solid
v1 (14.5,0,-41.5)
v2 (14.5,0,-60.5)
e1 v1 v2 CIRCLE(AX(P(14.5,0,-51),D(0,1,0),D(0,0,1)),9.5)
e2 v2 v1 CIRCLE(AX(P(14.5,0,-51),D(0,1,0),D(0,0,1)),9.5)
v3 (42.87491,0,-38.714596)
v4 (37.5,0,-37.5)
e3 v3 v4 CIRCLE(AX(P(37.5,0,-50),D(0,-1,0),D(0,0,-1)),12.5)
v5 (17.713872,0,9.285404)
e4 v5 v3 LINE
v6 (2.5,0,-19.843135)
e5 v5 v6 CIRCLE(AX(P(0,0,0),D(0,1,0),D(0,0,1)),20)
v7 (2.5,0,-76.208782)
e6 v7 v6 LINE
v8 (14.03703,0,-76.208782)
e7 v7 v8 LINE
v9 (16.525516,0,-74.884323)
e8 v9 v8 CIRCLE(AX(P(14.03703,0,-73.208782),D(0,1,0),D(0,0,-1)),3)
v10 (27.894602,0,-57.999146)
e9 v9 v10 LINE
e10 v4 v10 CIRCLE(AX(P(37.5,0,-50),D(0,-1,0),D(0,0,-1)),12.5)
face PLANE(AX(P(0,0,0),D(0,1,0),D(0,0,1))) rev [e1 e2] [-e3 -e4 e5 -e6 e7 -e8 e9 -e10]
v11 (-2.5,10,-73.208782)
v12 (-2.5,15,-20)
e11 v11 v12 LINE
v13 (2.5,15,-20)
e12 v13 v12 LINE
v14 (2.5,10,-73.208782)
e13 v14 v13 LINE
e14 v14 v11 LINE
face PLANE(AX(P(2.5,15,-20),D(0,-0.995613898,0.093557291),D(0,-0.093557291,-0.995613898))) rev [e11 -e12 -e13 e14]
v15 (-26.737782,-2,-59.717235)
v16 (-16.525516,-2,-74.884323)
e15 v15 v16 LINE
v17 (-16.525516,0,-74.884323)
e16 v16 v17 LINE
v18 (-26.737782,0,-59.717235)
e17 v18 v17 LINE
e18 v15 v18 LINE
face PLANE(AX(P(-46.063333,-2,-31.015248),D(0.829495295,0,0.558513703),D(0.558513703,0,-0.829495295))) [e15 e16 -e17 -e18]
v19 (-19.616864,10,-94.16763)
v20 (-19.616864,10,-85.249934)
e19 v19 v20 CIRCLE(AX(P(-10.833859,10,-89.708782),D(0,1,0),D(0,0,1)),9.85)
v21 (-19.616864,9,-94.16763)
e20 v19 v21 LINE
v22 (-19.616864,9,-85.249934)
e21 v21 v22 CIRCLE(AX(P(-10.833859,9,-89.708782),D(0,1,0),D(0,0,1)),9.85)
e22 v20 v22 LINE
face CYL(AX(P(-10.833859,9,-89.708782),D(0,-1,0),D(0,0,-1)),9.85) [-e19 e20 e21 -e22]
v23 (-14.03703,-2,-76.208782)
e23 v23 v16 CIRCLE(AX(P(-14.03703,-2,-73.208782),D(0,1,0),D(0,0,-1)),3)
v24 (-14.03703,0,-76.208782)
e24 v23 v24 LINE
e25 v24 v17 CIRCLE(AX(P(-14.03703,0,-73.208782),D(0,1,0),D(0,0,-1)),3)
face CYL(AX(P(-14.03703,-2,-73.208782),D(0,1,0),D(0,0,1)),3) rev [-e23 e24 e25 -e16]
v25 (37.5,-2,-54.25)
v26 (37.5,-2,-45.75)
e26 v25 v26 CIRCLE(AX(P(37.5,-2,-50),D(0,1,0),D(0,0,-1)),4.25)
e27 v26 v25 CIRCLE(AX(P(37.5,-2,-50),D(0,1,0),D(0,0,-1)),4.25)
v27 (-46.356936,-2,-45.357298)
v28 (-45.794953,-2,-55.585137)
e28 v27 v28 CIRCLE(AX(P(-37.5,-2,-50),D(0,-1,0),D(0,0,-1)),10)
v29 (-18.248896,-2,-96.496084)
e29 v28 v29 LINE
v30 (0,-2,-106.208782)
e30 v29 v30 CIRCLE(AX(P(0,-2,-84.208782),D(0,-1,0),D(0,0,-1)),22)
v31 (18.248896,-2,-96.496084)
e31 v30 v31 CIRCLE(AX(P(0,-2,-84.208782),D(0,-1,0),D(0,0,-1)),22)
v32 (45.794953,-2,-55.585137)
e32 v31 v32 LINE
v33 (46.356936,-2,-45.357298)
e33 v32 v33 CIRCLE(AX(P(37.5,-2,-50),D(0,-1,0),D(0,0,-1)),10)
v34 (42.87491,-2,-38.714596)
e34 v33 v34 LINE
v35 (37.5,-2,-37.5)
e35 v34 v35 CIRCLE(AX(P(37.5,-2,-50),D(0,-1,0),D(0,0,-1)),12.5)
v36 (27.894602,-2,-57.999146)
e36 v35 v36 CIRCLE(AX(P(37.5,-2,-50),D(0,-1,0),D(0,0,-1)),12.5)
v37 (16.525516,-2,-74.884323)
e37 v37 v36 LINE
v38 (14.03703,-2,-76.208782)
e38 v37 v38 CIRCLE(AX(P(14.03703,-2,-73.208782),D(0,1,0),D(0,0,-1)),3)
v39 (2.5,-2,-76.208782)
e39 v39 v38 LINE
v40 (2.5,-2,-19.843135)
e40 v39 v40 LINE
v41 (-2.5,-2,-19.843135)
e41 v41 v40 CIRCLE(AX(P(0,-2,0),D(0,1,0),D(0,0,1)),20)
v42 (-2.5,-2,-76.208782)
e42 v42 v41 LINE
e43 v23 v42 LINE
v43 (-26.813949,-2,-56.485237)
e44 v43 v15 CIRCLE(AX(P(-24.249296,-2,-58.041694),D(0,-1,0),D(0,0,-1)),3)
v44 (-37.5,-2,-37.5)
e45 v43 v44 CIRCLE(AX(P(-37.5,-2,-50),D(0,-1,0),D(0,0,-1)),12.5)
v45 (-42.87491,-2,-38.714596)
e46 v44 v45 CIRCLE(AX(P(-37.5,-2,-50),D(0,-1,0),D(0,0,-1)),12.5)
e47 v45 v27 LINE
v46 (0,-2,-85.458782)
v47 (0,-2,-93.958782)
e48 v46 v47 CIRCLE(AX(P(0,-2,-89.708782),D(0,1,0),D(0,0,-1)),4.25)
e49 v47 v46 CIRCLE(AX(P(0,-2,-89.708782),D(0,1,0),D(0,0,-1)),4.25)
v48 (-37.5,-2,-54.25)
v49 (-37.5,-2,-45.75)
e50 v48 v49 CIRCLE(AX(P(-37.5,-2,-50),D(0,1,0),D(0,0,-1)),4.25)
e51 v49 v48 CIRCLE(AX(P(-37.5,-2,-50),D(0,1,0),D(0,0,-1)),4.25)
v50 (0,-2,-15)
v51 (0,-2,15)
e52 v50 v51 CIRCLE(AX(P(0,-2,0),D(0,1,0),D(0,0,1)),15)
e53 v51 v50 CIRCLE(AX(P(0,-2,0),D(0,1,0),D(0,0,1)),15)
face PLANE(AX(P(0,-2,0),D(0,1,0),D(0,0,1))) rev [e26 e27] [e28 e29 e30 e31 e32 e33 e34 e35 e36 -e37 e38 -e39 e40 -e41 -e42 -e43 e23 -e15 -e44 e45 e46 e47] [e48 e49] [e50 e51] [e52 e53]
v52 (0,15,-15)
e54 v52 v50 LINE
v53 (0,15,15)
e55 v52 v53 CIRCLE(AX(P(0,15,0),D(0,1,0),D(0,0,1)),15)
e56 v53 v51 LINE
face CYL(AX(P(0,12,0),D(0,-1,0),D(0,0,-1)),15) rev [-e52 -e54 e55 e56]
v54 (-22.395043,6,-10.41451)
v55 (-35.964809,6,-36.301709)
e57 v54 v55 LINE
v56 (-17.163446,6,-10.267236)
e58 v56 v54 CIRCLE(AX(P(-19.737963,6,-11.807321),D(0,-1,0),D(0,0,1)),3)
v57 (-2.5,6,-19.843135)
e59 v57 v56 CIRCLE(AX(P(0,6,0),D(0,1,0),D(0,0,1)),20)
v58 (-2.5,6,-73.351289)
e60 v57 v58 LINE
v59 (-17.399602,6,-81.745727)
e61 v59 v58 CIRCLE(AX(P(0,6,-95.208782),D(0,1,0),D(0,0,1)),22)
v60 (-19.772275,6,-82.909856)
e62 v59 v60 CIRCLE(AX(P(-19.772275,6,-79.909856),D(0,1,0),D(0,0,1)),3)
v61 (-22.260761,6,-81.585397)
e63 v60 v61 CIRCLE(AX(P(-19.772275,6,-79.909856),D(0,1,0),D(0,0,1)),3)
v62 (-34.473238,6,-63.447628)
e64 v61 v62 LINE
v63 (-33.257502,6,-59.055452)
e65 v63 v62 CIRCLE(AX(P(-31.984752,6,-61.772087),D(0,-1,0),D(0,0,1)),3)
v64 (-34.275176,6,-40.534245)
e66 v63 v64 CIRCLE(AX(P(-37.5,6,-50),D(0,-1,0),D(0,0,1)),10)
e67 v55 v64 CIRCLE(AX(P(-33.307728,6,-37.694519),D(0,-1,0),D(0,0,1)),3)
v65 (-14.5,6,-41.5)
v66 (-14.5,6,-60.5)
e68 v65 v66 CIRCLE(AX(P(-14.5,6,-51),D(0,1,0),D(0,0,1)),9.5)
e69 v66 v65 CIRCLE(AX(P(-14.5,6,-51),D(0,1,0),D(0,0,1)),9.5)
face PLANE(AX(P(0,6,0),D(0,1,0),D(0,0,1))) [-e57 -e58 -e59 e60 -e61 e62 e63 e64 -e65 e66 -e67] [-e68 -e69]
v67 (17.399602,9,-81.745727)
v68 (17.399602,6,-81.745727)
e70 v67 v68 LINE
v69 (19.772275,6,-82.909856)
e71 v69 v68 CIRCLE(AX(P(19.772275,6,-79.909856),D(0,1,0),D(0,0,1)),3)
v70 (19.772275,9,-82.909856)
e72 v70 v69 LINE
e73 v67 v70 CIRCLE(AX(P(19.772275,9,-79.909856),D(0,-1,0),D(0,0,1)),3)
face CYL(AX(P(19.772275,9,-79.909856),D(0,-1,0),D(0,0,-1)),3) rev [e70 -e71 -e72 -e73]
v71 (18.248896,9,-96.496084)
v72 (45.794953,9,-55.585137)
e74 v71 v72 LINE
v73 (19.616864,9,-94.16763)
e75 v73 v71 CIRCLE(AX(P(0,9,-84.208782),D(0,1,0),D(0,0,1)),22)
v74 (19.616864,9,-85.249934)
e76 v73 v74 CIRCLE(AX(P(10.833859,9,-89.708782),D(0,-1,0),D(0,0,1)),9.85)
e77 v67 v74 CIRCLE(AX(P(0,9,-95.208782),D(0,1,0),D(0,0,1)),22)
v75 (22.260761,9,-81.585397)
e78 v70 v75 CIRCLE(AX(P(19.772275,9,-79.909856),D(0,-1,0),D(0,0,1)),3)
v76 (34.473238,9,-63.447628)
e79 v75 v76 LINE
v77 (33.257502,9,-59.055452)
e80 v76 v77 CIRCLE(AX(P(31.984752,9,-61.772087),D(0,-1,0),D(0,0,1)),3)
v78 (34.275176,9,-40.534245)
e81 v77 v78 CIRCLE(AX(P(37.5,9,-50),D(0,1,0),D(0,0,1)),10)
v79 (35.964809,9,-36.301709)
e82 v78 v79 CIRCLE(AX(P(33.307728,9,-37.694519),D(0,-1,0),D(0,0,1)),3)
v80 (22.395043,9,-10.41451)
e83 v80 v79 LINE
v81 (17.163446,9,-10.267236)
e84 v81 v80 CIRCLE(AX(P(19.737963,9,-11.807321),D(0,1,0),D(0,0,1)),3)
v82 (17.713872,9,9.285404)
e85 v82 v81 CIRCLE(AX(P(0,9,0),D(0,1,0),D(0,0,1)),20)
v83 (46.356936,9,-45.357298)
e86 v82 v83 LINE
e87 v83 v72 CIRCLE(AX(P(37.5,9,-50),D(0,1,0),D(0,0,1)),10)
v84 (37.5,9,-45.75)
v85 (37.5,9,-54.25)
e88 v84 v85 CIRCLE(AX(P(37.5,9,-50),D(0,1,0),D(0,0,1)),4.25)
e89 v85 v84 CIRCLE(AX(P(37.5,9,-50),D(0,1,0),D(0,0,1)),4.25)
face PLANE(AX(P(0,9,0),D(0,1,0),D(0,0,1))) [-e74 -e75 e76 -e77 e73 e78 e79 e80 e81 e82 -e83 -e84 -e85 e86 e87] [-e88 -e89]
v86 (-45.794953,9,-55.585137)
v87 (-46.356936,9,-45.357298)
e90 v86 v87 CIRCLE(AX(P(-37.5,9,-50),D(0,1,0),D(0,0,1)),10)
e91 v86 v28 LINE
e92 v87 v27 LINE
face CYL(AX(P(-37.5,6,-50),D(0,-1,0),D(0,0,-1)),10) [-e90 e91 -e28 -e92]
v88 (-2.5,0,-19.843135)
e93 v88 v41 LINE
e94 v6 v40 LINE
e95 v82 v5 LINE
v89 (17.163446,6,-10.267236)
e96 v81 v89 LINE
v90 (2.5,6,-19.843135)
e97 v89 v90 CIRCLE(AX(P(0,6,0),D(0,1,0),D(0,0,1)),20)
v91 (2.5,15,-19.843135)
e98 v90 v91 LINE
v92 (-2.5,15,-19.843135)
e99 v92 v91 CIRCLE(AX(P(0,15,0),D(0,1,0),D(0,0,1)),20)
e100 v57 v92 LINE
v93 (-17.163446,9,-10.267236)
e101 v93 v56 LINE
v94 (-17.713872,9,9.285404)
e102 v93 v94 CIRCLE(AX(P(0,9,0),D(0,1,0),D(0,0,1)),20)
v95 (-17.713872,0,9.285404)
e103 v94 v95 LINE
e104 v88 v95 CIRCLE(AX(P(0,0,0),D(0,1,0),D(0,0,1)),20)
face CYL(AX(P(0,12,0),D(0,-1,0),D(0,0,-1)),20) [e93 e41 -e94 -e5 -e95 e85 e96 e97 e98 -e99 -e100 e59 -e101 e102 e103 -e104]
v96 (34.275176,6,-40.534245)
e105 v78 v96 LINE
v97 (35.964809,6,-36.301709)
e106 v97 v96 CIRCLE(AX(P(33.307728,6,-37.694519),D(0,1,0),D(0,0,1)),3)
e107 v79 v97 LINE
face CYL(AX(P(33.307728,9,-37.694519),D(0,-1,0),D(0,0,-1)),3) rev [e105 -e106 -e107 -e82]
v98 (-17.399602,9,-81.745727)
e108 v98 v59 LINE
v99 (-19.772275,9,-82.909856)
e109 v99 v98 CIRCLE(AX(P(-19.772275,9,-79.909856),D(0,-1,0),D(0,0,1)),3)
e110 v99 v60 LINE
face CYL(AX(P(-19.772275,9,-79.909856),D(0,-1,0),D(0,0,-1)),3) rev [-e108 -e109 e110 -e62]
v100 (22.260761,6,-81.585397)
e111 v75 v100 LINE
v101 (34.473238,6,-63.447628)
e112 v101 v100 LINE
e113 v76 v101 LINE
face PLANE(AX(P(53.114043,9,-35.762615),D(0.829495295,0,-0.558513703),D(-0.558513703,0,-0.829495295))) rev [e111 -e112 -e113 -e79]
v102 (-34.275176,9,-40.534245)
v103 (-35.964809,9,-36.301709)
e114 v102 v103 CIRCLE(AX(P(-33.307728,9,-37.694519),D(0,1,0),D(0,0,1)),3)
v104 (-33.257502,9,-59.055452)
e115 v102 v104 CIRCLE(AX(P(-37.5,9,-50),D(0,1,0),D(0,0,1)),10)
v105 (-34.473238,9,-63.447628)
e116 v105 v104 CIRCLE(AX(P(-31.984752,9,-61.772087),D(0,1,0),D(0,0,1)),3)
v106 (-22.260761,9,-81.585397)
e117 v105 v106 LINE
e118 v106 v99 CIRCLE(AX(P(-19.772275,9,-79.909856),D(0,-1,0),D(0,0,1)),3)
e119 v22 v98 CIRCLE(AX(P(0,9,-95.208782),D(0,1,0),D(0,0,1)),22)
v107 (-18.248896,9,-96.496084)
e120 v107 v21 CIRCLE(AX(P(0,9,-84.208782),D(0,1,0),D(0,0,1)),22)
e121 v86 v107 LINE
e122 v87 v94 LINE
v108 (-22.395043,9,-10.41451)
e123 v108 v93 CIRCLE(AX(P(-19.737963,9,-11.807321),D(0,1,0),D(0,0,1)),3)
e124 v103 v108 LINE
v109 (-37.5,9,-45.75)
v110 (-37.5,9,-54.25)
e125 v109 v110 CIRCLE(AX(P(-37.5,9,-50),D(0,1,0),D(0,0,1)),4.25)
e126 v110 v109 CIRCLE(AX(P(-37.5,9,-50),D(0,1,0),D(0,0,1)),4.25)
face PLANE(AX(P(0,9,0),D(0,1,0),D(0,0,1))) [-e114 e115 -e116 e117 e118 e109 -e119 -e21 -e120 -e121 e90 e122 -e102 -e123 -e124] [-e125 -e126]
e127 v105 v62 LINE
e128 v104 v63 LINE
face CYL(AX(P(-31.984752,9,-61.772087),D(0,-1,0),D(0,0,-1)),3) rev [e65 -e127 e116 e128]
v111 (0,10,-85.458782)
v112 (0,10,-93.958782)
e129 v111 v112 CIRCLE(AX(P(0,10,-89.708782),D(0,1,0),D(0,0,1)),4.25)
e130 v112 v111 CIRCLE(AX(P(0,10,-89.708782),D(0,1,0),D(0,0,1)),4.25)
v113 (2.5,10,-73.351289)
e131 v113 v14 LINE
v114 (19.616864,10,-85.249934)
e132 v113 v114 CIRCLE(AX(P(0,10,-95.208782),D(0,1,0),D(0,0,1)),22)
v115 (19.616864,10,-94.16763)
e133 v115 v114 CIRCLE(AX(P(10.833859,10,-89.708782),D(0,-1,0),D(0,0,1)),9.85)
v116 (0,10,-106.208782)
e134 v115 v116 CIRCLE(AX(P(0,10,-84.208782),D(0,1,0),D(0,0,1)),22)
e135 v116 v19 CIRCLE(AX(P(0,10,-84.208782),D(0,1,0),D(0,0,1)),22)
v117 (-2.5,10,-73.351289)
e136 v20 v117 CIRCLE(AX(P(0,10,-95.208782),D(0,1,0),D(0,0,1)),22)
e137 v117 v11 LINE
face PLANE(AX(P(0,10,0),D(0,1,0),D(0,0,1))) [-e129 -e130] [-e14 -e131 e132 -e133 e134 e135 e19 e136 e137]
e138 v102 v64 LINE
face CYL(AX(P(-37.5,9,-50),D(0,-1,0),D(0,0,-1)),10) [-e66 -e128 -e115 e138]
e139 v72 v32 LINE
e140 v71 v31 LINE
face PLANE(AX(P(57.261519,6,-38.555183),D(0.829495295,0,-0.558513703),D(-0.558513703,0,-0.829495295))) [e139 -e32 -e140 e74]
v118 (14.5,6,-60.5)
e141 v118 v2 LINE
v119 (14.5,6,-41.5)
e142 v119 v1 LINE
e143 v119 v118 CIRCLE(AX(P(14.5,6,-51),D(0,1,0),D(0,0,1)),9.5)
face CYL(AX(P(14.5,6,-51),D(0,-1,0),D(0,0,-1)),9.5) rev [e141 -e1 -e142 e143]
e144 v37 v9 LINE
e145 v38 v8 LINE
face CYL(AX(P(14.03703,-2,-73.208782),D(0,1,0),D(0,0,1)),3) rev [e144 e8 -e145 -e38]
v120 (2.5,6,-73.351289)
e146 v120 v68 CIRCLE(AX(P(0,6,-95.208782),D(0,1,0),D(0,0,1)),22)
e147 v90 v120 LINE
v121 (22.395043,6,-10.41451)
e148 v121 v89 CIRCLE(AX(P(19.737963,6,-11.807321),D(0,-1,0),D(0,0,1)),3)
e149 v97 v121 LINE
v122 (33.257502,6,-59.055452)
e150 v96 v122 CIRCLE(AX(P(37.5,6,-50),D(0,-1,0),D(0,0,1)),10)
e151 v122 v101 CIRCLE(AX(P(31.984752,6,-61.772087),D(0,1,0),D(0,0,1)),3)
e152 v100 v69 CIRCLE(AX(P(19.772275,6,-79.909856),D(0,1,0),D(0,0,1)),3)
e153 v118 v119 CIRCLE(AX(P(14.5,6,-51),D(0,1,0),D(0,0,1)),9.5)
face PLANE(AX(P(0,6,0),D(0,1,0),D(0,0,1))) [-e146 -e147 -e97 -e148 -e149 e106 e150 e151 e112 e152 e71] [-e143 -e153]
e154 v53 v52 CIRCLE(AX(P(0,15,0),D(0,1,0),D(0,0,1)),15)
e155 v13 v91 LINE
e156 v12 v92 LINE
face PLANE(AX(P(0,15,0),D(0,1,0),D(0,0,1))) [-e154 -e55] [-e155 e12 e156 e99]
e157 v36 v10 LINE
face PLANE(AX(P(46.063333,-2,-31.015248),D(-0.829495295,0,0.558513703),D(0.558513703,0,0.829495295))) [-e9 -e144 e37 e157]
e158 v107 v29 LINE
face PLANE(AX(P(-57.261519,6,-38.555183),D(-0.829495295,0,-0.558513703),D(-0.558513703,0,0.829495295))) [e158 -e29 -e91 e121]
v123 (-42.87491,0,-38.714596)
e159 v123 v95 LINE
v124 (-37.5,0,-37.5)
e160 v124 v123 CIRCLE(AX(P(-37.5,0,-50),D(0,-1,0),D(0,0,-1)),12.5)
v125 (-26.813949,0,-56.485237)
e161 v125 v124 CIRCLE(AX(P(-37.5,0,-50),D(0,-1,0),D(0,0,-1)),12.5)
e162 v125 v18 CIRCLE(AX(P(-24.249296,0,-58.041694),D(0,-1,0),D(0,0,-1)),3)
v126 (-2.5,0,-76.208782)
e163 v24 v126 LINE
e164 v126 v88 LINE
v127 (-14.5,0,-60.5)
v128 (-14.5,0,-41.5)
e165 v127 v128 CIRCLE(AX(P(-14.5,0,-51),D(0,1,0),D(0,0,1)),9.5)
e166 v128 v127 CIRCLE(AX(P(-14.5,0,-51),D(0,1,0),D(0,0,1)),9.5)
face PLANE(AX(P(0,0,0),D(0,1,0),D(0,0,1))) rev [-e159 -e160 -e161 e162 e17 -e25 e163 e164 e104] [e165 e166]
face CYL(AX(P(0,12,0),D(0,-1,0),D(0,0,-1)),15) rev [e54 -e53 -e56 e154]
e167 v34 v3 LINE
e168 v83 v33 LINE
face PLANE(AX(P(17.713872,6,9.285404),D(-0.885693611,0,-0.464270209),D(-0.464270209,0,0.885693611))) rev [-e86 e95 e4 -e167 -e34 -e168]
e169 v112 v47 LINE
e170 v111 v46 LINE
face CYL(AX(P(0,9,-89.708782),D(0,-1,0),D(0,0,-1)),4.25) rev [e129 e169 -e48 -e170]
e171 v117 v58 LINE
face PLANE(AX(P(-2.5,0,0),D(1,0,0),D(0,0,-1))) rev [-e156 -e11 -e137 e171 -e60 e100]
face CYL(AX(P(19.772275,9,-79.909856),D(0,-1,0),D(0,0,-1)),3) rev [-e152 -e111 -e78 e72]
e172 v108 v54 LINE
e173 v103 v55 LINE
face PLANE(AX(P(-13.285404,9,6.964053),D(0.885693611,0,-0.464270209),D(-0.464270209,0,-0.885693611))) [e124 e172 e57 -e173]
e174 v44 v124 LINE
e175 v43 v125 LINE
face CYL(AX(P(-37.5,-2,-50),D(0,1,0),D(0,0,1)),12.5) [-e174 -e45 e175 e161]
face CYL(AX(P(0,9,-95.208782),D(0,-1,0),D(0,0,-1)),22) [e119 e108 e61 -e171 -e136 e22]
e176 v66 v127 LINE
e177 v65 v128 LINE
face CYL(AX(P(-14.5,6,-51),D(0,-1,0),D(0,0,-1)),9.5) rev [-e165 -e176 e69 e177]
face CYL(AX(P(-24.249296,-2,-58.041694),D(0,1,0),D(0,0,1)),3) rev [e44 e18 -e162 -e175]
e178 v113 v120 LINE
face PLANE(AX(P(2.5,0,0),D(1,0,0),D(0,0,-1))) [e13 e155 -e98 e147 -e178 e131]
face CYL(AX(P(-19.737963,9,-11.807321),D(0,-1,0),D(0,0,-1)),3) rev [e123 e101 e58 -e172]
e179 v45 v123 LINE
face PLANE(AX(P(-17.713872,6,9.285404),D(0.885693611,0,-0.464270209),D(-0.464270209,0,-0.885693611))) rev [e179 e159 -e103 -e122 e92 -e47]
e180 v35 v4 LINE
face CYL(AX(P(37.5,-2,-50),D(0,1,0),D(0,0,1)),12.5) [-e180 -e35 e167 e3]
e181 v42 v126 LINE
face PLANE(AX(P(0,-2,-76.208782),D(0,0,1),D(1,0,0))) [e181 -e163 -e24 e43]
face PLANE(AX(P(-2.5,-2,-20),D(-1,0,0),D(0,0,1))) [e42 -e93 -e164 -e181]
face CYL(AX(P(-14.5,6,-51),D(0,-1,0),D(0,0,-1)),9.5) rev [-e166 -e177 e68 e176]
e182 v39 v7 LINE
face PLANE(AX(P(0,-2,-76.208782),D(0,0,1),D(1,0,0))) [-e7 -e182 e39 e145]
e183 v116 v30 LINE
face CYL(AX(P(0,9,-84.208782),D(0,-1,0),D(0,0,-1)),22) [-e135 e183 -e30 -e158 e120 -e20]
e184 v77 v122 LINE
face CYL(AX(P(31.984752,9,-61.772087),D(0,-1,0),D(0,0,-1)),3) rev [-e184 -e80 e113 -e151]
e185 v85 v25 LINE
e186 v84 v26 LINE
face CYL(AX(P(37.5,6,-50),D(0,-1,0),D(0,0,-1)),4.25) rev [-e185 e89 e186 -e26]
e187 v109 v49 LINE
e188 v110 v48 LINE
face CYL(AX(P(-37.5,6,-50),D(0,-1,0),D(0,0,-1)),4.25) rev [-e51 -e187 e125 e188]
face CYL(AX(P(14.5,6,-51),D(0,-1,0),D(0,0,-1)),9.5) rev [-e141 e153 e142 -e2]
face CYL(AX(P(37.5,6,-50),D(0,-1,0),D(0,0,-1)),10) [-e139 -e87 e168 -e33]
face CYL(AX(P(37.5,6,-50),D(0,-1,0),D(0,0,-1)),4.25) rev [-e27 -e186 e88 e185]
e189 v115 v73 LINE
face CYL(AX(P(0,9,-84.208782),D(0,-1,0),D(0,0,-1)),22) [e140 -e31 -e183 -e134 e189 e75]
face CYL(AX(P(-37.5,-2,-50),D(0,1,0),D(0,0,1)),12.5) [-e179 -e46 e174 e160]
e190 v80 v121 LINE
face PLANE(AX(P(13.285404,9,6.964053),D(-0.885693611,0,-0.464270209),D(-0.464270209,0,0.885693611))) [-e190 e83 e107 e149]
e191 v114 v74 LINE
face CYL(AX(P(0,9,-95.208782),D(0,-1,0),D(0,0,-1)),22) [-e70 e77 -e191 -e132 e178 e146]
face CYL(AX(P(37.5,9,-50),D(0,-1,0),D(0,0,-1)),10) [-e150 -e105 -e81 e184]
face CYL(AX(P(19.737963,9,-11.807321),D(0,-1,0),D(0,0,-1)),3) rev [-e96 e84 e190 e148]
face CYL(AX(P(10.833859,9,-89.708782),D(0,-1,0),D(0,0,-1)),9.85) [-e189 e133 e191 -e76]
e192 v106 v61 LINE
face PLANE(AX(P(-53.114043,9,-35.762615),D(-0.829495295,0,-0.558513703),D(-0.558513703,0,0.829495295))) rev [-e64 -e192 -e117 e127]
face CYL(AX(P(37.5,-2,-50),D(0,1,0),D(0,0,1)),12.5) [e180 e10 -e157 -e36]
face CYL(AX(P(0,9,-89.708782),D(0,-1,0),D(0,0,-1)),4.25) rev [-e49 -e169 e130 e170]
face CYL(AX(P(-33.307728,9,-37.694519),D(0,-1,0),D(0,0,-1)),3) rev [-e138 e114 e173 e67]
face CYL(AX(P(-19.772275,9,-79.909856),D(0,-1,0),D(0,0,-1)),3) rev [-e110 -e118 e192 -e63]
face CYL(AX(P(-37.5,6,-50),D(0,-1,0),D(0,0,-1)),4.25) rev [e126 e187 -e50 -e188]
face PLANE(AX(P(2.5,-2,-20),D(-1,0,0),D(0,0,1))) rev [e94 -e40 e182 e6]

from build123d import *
from build123d.topology import SkipClean

# Parameters (mm, degrees)
PLATE_CONTOURS_SKETCH_R      = 20
PLATE_CONTOURS_SKETCH_R_2    = 15
PLATE_BODY_12MM_DEPTH        = 12
SKETCH1_3_R                  = 4.25
PLATE_LEVEL_9MM_DEPTH        = 9
SKETCH1_4_R                  = 10
SKETCH1_4_R_2                = 4.25
SKETCH1_4_R_3                = 9.5
FLOOR_LEVEL_6MM_DEPTH        = 6
SKETCH1_5_R                  = 20
SKETCH1_5_R_2                = 15
HUB_BOSS_15MM_DEPTH          = 15
SKETCH1_6_R                  = 4.25
ROUND_BOSS_10MM_DEPTH        = 10
SKETCH1_7_R                  = 10
SKETCH1_7_R_2                = 4.25
CORNER_BOSS_LEVEL_9MM_DEPTH  = 9
SIDE_TAB_5MM_DEPTH           = 2.5
BOTTOM_START                 = -2
SKETCH1_8_R                  = 20
SKETCH1_8_R_2                = 15
BOTTOM_PAD_2MM_DEPTH         = 2
LIP_START                    = 2
LIP_PROFILE_SKETCH_R         = 4.25
LIP_2MM_DEPTH                = 2
HUB_CONNECTING_RIB_5MM_REACH = 119.582
HUB_RIB_PATH_SKETCH_WALLS_W  = 5
HUB_RIB_PATH_SKETCH_WALLS_H  = 293.373025838


with BuildPart() as part:
    # Plate Contours Sketch → Plate Body 12mm (new body)
    with BuildSketch(Plane(origin=(0, 0, 0), x_dir=(1, 0, 0), z_dir=(0, 1, 0))):
        with Locations(Location((0, 0, 0), (0, 0, 270))):
            Circle(PLATE_CONTOURS_SKETCH_R)
        with Locations(Location((0, 0, 0), (0, 0, 270))):
            Circle(PLATE_CONTOURS_SKETCH_R_2, mode=Mode.SUBTRACT)
    extrude(amount=PLATE_BODY_12MM_DEPTH)



with BuildPart() as body_2:
    # Sketch1_3 → Plate Level 9mm (new body)
    with BuildSketch(Plane(origin=(0, 0, 0), x_dir=(1, 0, 0), z_dir=(0, 1, 0))):
        with BuildLine():
            ThreePointArc((19.616863963, 94.1676298), (20.683858962, 89.708782064), (19.616863963, 85.249934327))
            ThreePointArc((19.616863963, 85.249934327), (0, 73.208782064), (-19.616863963, 85.249934327))
            ThreePointArc((-19.616863963, 85.249934327), (-20.683858962, 89.708782064), (-19.616863963, 94.1676298))
            ThreePointArc((-19.616863963, 94.1676298), (0, 106.208782064), (19.616863963, 94.1676298))
        make_face()
        with Locations(Location((0, 89.708782064, 0), (0, 0, 270))):
            Circle(SKETCH1_3_R, mode=Mode.SUBTRACT)
    extrude(amount=PLATE_LEVEL_9MM_DEPTH)


with BuildPart() as part_1:
    add(part.part)

    add(body_2.part)  # Floor Level 6mm merges body 2
    # Sketch1_4 → Floor Level 6mm (add)
    # profile 1 of 7: a face of its own
    with BuildSketch(Plane(origin=(0, 0, 0), x_dir=(1, 0, 0), z_dir=(0, 1, 0))):
        with BuildLine():
            ThreePointArc((-34.275175703, 40.5342455), (-41.207509883, 40.712676894), (-46.356936115, 45.357297914))
            Line((-46.356936115, 45.357297914), (-17.713872229, -9.285404172))
            ThreePointArc((-17.713872229, -9.285404172), (-19.992079916, 0.562797133), (-17.163445775, 10.26723571))
            ThreePointArc((-17.163445775, 10.26723571), (-19.822382211, 8.808509079), (-22.395043476, 10.414510441))
            Line((-22.395043476, 10.414510441), (-35.964809248, 36.301708524))
            ThreePointArc((-35.964809248, 36.301708524), (-36.093925346, 38.806772115), (-34.275175703, 40.5342455))
        make_face()
    # profile 2 of 7: a face of its own
    with BuildSketch(Plane(origin=(0, 0, 0), x_dir=(1, 0, 0), z_dir=(0, 1, 0))):
        with Locations((-37.5, 50)):
            Circle(SKETCH1_4_R)
        with Locations(Location((-37.5, 50, 0), (0, 0, 270))):
            Circle(SKETCH1_4_R_2, mode=Mode.SUBTRACT)
    # profile 3 of 7: a face of its own
    with BuildSketch(Plane(origin=(0, 0, 0), x_dir=(1, 0, 0), z_dir=(0, 1, 0))):
        with BuildLine():
            Line((-18.248896479, 96.496083529), (-45.794952945, 55.58513703))
            ThreePointArc((-45.794952945, 55.58513703), (-40.167652212, 59.637615456), (-33.257501674, 59.055451836))
            ThreePointArc((-33.257501674, 59.055451836), (-34.876036813, 60.971791723), (-34.47323806, 63.447628496))
            Line((-34.47323806, 63.447628496), (-22.26076094, 81.585397097))
            ThreePointArc((-22.26076094, 81.585397097), (-19.871166838, 82.908225614), (-17.39960205, 81.745727117))
            ThreePointArc((-17.39960205, 81.745727117), (-18.590980503, 83.445472839), (-19.616863963, 85.249934327))
            ThreePointArc((-19.616863963, 85.249934327), (-20.683858962, 89.708782064), (-19.616863963, 94.1676298))
            ThreePointArc((-19.616863963, 94.1676298), (-18.968641956, 95.352866698), (-18.248896479, 96.496083529))
        make_face()
    # profile 4 of 7: a face of its own
    with BuildSketch(Plane(origin=(0, 0, 0), x_dir=(1, 0, 0), z_dir=(0, 1, 0))):
        with BuildLine():
            Line((45.794952945, 55.58513703), (18.248896479, 96.496083529))
            ThreePointArc((18.248896479, 96.496083529), (18.968641956, 95.352866698), (19.616863963, 94.1676298))
            ThreePointArc((19.616863963, 94.1676298), (20.683858962, 89.708782064), (19.616863963, 85.249934327))
            ThreePointArc((19.616863963, 85.249934327), (18.590980503, 83.445472839), (17.39960205, 81.745727117))
            ThreePointArc((17.39960205, 81.745727117), (19.871166838, 82.908225614), (22.26076094, 81.585397097))
            Line((22.26076094, 81.585397097), (34.47323806, 63.447628496))
            ThreePointArc((34.47323806, 63.447628496), (34.876036813, 60.971791723), (33.257501674, 59.055451836))
            ThreePointArc((33.257501674, 59.055451836), (40.167652212, 59.637615456), (45.794952945, 55.58513703))
        make_face()
    # profile 5 of 7: a face of its own
    with BuildSketch(Plane(origin=(0, 0, 0), x_dir=(1, 0, 0), z_dir=(0, 1, 0))):
        with Locations((37.5, 50)):
            Circle(SKETCH1_4_R)
        with Locations(Location((37.5, 50, 0), (0, 0, 270))):
            Circle(SKETCH1_4_R_2, mode=Mode.SUBTRACT)
    # profile 6 of 7: a face of its own
    with BuildSketch(Plane(origin=(0, 0, 0), x_dir=(1, 0, 0), z_dir=(0, 1, 0))):
        with BuildLine():
            ThreePointArc((20, 0), (19.420059791, -4.781346851), (17.713872229, -9.285404172))
            Line((17.713872229, -9.285404172), (46.356936115, 45.357297914))
            ThreePointArc((46.356936115, 45.357297914), (41.207509883, 40.712676894), (34.275175703, 40.5342455))
            ThreePointArc((34.275175703, 40.5342455), (36.093925346, 38.806772115), (35.964809248, 36.301708524))
            Line((35.964809248, 36.301708524), (22.395043476, 10.414510441))
            ThreePointArc((22.395043476, 10.414510441), (19.822382211, 8.808509079), (17.163445775, 10.26723571))
            ThreePointArc((17.163445775, 10.26723571), (19.277822951, 5.325931116), (20, 0))
        make_face()
    # profile 7 of 7: a face of its own
    with BuildSketch(Plane(origin=(0, 0, 0), x_dir=(1, 0, 0), z_dir=(0, 1, 0))):
        with BuildLine():
            ThreePointArc((-34.47323806, 63.447628496), (-34.876036813, 60.971791723), (-33.257501674, 59.055451836))
            ThreePointArc((-33.257501674, 59.055451836), (-29.061250589, 55.365399181), (-27.5, 50))
            ThreePointArc((-27.5, 50), (-29.368326034, 44.179701166), (-34.275175703, 40.5342455))
            ThreePointArc((-34.275175703, 40.5342455), (-36.093925346, 38.806772115), (-35.964809248, 36.301708524))
            Line((-35.964809248, 36.301708524), (-22.395043476, 10.414510441))
            ThreePointArc((-22.395043476, 10.414510441), (-19.822382211, 8.808509079), (-17.163445775, 10.26723571))
            ThreePointArc((-17.163445775, 10.26723571), (0, 20), (17.163445775, 10.26723571))
            ThreePointArc((17.163445775, 10.26723571), (19.822382211, 8.808509079), (22.395043476, 10.414510441))
            Line((22.395043476, 10.414510441), (35.964809248, 36.301708524))
            ThreePointArc((35.964809248, 36.301708524), (36.093925346, 38.806772115), (34.275175703, 40.5342455))
            ThreePointArc((34.275175703, 40.5342455), (27.515061451, 49.451363348), (33.257501674, 59.055451836))
            ThreePointArc((33.257501674, 59.055451836), (34.876036813, 60.971791723), (34.47323806, 63.447628496))
            Line((34.47323806, 63.447628496), (22.26076094, 81.585397097))
            ThreePointArc((22.26076094, 81.585397097), (19.871166838, 82.908225614), (17.39960205, 81.745727117))
            ThreePointArc((17.39960205, 81.745727117), (0, 73.208782064), (-17.39960205, 81.745727117))
            ThreePointArc((-17.39960205, 81.745727117), (-19.871166838, 82.908225614), (-22.26076094, 81.585397097))
            Line((-22.26076094, 81.585397097), (-34.47323806, 63.447628496))
        make_face()
        with Locations(Location((-14.5, 51, 0), (0, 0, 270))):
            Circle(SKETCH1_4_R_3, mode=Mode.SUBTRACT)
        with Locations(Location((14.5, 51, 0), (0, 0, 270))):
            Circle(SKETCH1_4_R_3, mode=Mode.SUBTRACT)
    extrude(amount=FLOOR_LEVEL_6MM_DEPTH)

    # Sketch1_5 → Hub Boss 15mm (add)
    with BuildSketch(Plane(origin=(0, 0, 0), x_dir=(1, 0, 0), z_dir=(0, 1, 0))):
        with Locations(Location((0, 0, 0), (0, 0, 332.336998576))):
            Circle(SKETCH1_5_R)
        with Locations(Location((0, 0, 0), (0, 0, 270))):
            Circle(SKETCH1_5_R_2, mode=Mode.SUBTRACT)
    extrude(amount=HUB_BOSS_15MM_DEPTH)

    # Sketch1_6 → Round Boss 10mm (add)
    with BuildSketch(Plane(origin=(0, 0, 0), x_dir=(1, 0, 0), z_dir=(0, 1, 0))):
        with BuildLine():
            ThreePointArc((19.616863963, 94.1676298), (20.683858962, 89.708782064), (19.616863963, 85.249934327))
            ThreePointArc((19.616863963, 85.249934327), (0, 73.208782064), (-19.616863963, 85.249934327))
            ThreePointArc((-19.616863963, 85.249934327), (-20.683858962, 89.708782064), (-19.616863963, 94.1676298))
            ThreePointArc((-19.616863963, 94.1676298), (0, 106.208782064), (19.616863963, 94.1676298))
        make_face()
        with Locations(Location((0, 89.708782064, 0), (0, 0, 270))):
            Circle(SKETCH1_6_R, mode=Mode.SUBTRACT)
    extrude(amount=ROUND_BOSS_10MM_DEPTH)

    # Sketch1_7 → Corner Boss Level 9mm (add)
    # profile 1 of 6: a face of its own
    with BuildSketch(Plane(origin=(0, 0, 0), x_dir=(1, 0, 0), z_dir=(0, 1, 0))):
        with BuildLine():
            ThreePointArc((-34.275175703, 40.5342455), (-41.207509883, 40.712676894), (-46.356936115, 45.357297914))
            Line((-46.356936115, 45.357297914), (-17.713872229, -9.285404172))
            ThreePointArc((-17.713872229, -9.285404172), (-19.992079916, 0.562797133), (-17.163445775, 10.26723571))
            ThreePointArc((-17.163445775, 10.26723571), (-19.822382211, 8.808509079), (-22.395043476, 10.414510441))
            Line((-22.395043476, 10.414510441), (-35.964809248, 36.301708524))
            ThreePointArc((-35.964809248, 36.301708524), (-36.093925346, 38.806772115), (-34.275175703, 40.5342455))
        make_face()
    # profile 2 of 6: a face of its own
    with BuildSketch(Plane(origin=(0, 0, 0), x_dir=(1, 0, 0), z_dir=(0, 1, 0))):
        with Locations((-37.5, 50)):
            Circle(SKETCH1_7_R)
        with Locations(Location((-37.5, 50, 0), (0, 0, 270))):
            Circle(SKETCH1_7_R_2, mode=Mode.SUBTRACT)
    # profile 3 of 6: a face of its own
    with BuildSketch(Plane(origin=(0, 0, 0), x_dir=(1, 0, 0), z_dir=(0, 1, 0))):
        with BuildLine():
            Line((-18.248896479, 96.496083529), (-45.794952945, 55.58513703))
            ThreePointArc((-45.794952945, 55.58513703), (-40.167652212, 59.637615456), (-33.257501674, 59.055451836))
            ThreePointArc((-33.257501674, 59.055451836), (-34.876036813, 60.971791723), (-34.47323806, 63.447628496))
            Line((-34.47323806, 63.447628496), (-22.26076094, 81.585397097))
            ThreePointArc((-22.26076094, 81.585397097), (-19.871166838, 82.908225614), (-17.39960205, 81.745727117))
            ThreePointArc((-17.39960205, 81.745727117), (-18.590980503, 83.445472839), (-19.616863963, 85.249934327))
            ThreePointArc((-19.616863963, 85.249934327), (-20.683858962, 89.708782064), (-19.616863963, 94.1676298))
            ThreePointArc((-19.616863963, 94.1676298), (-18.968641956, 95.352866698), (-18.248896479, 96.496083529))
        make_face()
    # profile 4 of 6: a face of its own
    with BuildSketch(Plane(origin=(0, 0, 0), x_dir=(1, 0, 0), z_dir=(0, 1, 0))):
        with BuildLine():
            Line((45.794952945, 55.58513703), (18.248896479, 96.496083529))
            ThreePointArc((18.248896479, 96.496083529), (18.968641956, 95.352866698), (19.616863963, 94.1676298))
            ThreePointArc((19.616863963, 94.1676298), (20.683858962, 89.708782064), (19.616863963, 85.249934327))
            ThreePointArc((19.616863963, 85.249934327), (18.590980503, 83.445472839), (17.39960205, 81.745727117))
            ThreePointArc((17.39960205, 81.745727117), (19.871166838, 82.908225614), (22.26076094, 81.585397097))
            Line((22.26076094, 81.585397097), (34.47323806, 63.447628496))
            ThreePointArc((34.47323806, 63.447628496), (34.876036813, 60.971791723), (33.257501674, 59.055451836))
            ThreePointArc((33.257501674, 59.055451836), (40.167652212, 59.637615456), (45.794952945, 55.58513703))
        make_face()
    # profile 5 of 6: a face of its own
    with BuildSketch(Plane(origin=(0, 0, 0), x_dir=(1, 0, 0), z_dir=(0, 1, 0))):
        with Locations((37.5, 50)):
            Circle(SKETCH1_7_R)
        with Locations(Location((37.5, 50, 0), (0, 0, 270))):
            Circle(SKETCH1_7_R_2, mode=Mode.SUBTRACT)
    # profile 6 of 6: a face of its own
    with BuildSketch(Plane(origin=(0, 0, 0), x_dir=(1, 0, 0), z_dir=(0, 1, 0))):
        with BuildLine():
            ThreePointArc((20, 0), (19.420059791, -4.781346851), (17.713872229, -9.285404172))
            Line((17.713872229, -9.285404172), (46.356936115, 45.357297914))
            ThreePointArc((46.356936115, 45.357297914), (41.207509883, 40.712676894), (34.275175703, 40.5342455))
            ThreePointArc((34.275175703, 40.5342455), (36.093925346, 38.806772115), (35.964809248, 36.301708524))
            Line((35.964809248, 36.301708524), (22.395043476, 10.414510441))
            ThreePointArc((22.395043476, 10.414510441), (19.822382211, 8.808509079), (17.163445775, 10.26723571))
            ThreePointArc((17.163445775, 10.26723571), (19.277822951, 5.325931116), (20, 0))
        make_face()
    extrude(amount=CORNER_BOSS_LEVEL_9MM_DEPTH)

    # Side Tab Sketch → Side Tab 5mm (add, symmetric)
    with BuildSketch(Plane(origin=(0, 0, 0), x_dir=(0, 0, -1), z_dir=(1, 0, 0))):
        Polygon((20, 15), (73.208782064, 10), (74.497408644, 10), (74.497408644, 5), (73.208782064, 5), (18, 5), (18, 15), align=None)
    extrude(amount=SIDE_TAB_5MM_DEPTH, both=True)

    # Sketch1_8 → Bottom Pad 2mm (add)
    with BuildSketch(Plane(origin=(0, 0, 0), x_dir=(1, 0, 0), z_dir=(0, 1, 0)).offset(BOTTOM_START)):
        with Locations(Location((0, 0, 0), (0, 0, 97.180755781))):
            Circle(SKETCH1_8_R)
        with Locations(Location((0, 0, 0), (0, 0, 270))):
            Circle(SKETCH1_8_R_2, mode=Mode.SUBTRACT)
    extrude(amount=BOTTOM_PAD_2MM_DEPTH)

    # Lip Profile Sketch → Lip 2mm (add)
    with SkipClean():  # the faces are left unmerged after this step: merging them gives an invalid solid
        with BuildSketch(Plane.XZ.offset(LIP_START)):
            with BuildLine():
                ThreePointArc((-46.356936115, -45.357297914), (-47.484938549, -50.548636652), (-45.794952945, -55.58513703))
                Line((-45.794952945, -55.58513703), (-18.248896479, -96.496083529))
                ThreePointArc((-18.248896479, -96.496083529), (0, -106.208782064), (18.248896479, -96.496083529))
                Line((18.248896479, -96.496083529), (45.794952945, -55.58513703))
                ThreePointArc((45.794952945, -55.58513703), (47.484938549, -50.548636652), (46.356936115, -45.357297914))
                Line((46.356936115, -45.357297914), (42.87490955, -38.714595828))
                ThreePointArc((42.87490955, -38.714595828), (27.628438686, -42.33173571), (27.894602034, -57.999145574))
                Line((27.894602034, -57.999145574), (16.525516364, -74.884323173))
                ThreePointArc((16.525516364, -74.884323173), (15.446529802, -75.857047848), (14.037030481, -76.208782064))
                Line((14.037030481, -76.208782064), (-14.037030481, -76.208782064))
                ThreePointArc((-14.037030481, -76.208782064), (-15.446529802, -75.857047848), (-16.525516364, -74.884323173))
                Line((-16.525516364, -74.884323173), (-26.737782046, -59.717235446))
                ThreePointArc((-26.737782046, -59.717235446), (-27.248463448, -58.112373832), (-26.813948518, -56.485237369))
                ThreePointArc((-26.813948518, -56.485237369), (-28.22632854, -41.618531295), (-42.87490955, -38.714595828))
                Line((-42.87490955, -38.714595828), (-46.356936115, -45.357297914))
            make_face()
            with Locations(Location((0, -89.708782064, 0), (0, 0, 270))):
                Circle(LIP_PROFILE_SKETCH_R, mode=Mode.SUBTRACT)
            with Locations(Location((-37.5, -50, 0), (0, 0, 270))):
                Circle(LIP_PROFILE_SKETCH_R, mode=Mode.SUBTRACT)
            with Locations(Location((37.5, -50, 0), (0, 0, 270))):
                Circle(LIP_PROFILE_SKETCH_R, mode=Mode.SUBTRACT)
        extrude(amount=-LIP_2MM_DEPTH)

    # Hub Rib Path Sketch walls → Hub Connecting Rib 5mm (add, up to next)
    with BuildSketch(Plane.XZ.offset(2), mode=Mode.PRIVATE) as hub_connecting_rib_5mm_sk1:
        with Locations((0, -48.104391032)):
            Rectangle(HUB_RIB_PATH_SKETCH_WALLS_W, HUB_RIB_PATH_SKETCH_WALLS_H)
    hub_connecting_rib_5mm_tool1 = extrude(hub_connecting_rib_5mm_sk1.sketch, amount=-HUB_CONNECTING_RIB_5MM_REACH, mode=Mode.PRIVATE) - part_1.part
    add(hub_connecting_rib_5mm_tool1.solids().sort_by_distance((0, -2, -48.104391032))[0])


solid = part_1.part
